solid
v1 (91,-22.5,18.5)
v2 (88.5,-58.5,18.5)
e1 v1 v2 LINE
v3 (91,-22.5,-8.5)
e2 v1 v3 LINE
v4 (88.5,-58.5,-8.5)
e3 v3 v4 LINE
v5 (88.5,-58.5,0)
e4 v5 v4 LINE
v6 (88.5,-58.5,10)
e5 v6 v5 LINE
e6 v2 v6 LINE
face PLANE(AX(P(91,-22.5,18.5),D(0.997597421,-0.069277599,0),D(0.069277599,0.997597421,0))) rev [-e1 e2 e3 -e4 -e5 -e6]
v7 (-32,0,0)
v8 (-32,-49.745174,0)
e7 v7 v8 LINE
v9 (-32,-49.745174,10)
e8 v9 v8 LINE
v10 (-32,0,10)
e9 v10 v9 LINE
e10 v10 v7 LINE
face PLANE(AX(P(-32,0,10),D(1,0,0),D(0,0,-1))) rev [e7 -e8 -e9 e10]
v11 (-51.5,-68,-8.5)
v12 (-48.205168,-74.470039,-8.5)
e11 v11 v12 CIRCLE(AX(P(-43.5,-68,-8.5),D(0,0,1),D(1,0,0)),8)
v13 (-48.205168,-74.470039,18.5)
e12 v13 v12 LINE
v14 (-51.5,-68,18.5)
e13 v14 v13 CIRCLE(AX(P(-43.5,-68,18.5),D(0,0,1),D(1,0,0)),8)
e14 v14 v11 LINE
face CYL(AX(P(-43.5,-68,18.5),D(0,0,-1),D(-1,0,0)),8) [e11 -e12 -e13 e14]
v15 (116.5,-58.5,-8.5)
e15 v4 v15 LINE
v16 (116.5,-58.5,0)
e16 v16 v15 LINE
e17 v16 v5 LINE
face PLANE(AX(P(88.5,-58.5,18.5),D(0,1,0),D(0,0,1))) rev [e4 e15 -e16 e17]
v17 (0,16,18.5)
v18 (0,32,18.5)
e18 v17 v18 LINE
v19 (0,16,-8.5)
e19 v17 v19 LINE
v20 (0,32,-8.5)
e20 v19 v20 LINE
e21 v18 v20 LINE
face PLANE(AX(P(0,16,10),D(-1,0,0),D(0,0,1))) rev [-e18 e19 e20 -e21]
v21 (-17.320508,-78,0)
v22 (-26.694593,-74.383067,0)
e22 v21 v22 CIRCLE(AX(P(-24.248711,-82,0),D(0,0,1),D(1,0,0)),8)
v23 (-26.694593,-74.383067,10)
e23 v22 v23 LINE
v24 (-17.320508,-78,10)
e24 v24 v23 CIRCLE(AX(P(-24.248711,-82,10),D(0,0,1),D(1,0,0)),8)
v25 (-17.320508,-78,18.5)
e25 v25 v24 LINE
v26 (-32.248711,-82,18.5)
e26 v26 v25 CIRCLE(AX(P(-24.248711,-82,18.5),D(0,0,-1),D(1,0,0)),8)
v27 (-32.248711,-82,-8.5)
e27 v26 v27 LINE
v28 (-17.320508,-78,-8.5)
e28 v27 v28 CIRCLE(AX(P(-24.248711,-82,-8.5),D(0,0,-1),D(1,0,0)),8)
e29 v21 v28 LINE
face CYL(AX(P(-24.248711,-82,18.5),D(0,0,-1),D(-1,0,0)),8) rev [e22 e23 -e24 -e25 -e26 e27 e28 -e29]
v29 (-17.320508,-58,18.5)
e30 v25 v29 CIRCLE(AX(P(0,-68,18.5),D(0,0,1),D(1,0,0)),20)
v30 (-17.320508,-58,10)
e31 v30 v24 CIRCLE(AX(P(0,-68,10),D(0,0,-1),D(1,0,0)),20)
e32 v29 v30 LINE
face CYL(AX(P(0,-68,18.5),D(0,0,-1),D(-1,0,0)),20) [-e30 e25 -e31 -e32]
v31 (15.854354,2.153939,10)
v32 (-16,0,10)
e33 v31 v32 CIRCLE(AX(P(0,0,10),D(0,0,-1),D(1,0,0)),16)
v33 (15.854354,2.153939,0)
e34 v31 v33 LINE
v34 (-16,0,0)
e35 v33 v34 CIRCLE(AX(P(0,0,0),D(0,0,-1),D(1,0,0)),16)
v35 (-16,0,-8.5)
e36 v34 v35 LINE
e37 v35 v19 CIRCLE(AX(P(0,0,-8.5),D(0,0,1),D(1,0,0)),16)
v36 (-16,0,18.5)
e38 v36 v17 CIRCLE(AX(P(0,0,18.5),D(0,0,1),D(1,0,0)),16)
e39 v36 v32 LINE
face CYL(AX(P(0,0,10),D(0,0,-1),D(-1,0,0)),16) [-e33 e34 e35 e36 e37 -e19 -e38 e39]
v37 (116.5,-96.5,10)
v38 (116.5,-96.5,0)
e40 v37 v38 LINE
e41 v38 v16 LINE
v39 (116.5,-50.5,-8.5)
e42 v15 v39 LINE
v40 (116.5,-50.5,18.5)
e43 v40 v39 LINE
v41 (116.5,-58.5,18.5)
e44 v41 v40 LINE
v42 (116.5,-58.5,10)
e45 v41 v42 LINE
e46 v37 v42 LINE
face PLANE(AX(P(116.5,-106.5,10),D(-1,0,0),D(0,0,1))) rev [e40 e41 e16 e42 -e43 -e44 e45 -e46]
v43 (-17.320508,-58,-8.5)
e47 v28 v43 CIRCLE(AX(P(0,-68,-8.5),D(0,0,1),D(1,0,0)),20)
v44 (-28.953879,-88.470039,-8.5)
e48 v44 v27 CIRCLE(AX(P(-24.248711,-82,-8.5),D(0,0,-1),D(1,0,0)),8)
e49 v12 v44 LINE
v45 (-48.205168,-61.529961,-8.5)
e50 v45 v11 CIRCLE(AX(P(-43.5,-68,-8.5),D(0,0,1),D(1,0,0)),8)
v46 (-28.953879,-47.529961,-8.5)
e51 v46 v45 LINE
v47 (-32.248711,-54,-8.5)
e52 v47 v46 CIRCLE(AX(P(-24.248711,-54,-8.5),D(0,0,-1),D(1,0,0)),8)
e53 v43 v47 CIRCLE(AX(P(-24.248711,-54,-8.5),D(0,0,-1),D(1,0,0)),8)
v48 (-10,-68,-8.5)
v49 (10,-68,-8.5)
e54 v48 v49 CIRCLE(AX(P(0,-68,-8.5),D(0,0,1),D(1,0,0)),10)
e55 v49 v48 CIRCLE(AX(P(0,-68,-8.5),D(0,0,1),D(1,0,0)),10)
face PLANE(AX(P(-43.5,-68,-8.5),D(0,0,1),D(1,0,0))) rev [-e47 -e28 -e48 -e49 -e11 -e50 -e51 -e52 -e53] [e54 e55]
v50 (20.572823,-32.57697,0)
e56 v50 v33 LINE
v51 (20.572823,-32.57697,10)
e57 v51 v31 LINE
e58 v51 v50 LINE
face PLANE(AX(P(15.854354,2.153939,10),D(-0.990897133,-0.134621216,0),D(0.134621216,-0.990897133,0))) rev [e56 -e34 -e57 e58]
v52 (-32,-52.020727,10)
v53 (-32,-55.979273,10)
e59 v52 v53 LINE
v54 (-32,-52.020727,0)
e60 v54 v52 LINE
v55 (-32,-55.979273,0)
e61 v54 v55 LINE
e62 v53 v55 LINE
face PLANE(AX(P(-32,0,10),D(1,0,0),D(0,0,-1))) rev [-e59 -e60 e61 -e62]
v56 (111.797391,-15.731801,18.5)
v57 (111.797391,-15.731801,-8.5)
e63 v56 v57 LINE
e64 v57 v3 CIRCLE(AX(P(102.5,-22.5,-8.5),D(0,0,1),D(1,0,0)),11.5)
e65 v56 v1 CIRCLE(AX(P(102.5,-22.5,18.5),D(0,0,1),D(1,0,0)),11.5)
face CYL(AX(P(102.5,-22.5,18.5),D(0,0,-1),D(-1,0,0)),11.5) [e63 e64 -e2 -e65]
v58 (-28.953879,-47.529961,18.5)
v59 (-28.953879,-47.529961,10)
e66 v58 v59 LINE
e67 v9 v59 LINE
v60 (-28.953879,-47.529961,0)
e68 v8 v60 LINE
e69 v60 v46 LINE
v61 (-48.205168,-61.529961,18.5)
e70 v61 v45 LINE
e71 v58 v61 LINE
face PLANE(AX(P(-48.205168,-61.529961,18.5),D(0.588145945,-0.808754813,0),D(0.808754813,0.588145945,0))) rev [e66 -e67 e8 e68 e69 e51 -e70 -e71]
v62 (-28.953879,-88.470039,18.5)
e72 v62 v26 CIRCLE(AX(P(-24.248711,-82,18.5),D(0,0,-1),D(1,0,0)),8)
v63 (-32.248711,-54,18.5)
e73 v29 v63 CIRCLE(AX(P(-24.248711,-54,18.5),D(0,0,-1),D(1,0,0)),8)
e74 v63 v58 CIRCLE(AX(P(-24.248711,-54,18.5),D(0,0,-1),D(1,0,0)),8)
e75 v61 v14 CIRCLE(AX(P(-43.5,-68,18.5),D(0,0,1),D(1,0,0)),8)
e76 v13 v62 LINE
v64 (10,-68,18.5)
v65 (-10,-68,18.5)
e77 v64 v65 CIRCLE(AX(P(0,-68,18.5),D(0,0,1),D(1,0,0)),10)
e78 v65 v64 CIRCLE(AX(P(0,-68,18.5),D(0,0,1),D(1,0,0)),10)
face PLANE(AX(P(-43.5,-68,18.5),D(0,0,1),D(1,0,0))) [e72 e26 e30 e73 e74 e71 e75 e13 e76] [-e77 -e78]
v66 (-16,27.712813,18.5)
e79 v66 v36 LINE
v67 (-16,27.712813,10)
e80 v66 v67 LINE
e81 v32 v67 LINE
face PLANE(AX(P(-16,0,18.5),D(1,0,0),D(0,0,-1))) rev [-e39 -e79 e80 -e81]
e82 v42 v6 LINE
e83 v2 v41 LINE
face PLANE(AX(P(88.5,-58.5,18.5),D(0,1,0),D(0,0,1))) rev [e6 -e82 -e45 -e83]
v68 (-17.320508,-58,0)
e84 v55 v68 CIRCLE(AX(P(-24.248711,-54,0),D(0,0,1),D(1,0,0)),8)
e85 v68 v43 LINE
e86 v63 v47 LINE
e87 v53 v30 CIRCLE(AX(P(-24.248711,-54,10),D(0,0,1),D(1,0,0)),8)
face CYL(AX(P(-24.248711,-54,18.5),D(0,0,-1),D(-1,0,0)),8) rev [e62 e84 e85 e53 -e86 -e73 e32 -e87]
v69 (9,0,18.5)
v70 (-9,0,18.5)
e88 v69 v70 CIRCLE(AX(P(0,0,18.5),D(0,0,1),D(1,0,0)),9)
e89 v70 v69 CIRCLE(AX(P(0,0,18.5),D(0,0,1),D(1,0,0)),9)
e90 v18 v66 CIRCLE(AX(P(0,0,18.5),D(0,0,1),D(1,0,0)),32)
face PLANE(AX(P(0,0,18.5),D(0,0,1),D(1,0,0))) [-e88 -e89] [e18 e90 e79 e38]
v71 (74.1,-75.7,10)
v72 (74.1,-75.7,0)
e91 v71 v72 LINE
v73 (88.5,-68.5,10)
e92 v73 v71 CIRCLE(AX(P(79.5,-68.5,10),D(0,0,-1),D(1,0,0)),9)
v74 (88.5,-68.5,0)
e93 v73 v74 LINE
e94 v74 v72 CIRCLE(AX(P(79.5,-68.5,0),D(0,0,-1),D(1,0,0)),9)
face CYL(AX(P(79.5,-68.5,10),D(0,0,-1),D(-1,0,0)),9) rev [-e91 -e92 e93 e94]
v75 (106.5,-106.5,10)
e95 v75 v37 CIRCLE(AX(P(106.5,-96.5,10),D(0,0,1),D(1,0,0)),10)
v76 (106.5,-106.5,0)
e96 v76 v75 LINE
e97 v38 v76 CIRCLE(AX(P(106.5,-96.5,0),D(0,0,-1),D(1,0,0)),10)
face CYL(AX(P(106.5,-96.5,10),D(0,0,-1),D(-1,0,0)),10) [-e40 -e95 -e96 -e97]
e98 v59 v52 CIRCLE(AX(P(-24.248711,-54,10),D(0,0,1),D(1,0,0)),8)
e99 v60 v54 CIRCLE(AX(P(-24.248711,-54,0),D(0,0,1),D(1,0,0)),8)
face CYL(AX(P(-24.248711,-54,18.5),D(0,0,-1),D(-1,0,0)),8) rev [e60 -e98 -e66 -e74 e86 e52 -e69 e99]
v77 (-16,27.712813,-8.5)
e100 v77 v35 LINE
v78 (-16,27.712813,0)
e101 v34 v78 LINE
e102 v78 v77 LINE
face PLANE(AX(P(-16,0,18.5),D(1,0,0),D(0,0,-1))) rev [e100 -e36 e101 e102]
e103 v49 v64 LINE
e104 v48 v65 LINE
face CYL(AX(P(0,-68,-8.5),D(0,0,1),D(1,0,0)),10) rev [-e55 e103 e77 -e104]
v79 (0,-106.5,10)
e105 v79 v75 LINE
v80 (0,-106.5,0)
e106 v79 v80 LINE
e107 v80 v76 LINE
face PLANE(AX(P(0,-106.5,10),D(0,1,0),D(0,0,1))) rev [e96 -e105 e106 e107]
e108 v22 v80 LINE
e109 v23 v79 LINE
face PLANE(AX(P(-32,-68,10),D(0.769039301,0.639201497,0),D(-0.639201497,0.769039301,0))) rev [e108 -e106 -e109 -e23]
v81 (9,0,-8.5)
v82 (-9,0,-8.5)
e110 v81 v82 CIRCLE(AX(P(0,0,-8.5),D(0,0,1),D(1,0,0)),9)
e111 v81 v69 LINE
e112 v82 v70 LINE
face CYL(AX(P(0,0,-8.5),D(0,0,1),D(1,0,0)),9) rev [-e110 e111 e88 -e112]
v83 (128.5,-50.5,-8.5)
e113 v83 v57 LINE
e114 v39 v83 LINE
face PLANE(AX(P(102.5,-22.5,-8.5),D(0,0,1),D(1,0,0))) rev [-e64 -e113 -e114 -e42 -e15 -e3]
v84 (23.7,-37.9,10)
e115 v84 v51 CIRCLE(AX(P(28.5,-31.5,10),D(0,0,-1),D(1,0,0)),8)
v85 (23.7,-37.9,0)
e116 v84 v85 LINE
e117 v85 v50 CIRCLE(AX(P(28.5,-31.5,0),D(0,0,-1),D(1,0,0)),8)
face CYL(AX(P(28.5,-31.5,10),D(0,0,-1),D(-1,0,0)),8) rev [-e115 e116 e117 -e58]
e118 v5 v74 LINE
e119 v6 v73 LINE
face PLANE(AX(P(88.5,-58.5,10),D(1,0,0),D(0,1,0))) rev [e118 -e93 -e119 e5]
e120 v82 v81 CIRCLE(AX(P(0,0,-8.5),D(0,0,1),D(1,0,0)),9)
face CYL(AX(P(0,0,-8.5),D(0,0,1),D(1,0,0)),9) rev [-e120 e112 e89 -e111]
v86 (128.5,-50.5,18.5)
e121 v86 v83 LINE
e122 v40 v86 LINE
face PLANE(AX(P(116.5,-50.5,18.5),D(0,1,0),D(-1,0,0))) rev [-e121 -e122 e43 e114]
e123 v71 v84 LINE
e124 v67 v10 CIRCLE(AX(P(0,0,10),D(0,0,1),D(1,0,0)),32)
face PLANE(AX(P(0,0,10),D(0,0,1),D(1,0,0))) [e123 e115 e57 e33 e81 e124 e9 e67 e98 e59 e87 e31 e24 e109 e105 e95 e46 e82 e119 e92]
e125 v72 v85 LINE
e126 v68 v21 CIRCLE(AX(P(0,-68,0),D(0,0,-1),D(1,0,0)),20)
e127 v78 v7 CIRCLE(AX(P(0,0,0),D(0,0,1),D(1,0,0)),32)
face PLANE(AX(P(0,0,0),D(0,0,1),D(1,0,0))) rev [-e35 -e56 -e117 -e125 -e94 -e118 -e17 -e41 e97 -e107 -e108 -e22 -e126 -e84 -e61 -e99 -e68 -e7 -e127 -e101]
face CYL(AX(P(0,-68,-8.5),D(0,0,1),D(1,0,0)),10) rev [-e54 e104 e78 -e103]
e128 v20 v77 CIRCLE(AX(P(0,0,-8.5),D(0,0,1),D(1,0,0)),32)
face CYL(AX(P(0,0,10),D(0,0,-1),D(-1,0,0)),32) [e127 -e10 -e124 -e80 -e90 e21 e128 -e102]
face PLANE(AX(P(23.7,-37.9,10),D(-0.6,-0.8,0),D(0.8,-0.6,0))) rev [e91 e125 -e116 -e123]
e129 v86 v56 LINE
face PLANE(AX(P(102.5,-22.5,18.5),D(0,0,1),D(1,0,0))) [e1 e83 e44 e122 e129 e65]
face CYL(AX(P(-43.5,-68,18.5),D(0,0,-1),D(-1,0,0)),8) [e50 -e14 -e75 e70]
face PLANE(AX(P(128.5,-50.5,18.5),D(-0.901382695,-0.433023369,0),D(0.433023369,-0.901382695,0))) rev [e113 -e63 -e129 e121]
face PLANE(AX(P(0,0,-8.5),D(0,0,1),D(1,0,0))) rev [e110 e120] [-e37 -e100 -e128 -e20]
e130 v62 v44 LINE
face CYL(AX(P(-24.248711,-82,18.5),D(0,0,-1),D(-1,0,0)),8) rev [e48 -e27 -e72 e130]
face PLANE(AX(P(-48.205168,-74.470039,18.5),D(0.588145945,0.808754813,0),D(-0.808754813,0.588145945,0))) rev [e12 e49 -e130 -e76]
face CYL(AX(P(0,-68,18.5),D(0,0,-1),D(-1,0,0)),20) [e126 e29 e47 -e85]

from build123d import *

# Parameters (mm, degrees)
BRACKET_PLATE_DEPTH        = 10
UPPER_PIVOT_BOSS_DEPTH     = 13.5
UPPER_PIVOT_BORE_PROFILE_R = 9
UPPER_PIVOT_BORE_18_DEPTH  = 27
LOWER_PIVOT_BOSS_DEPTH     = 13.5
LOWER_PIVOT_BORE_PROFILE_R = 10
LOWER_PIVOT_BORE_20_DEPTH  = 27
STOP_LUG_DEPTH             = 13.5
PLATE_FILLET_R10_R         = 10


with BuildPart() as part:
    # Bracket Plate Profile → Bracket Plate (new body)
    with BuildSketch(Plane.XY):
        with BuildLine():
            Line((-32, 0), (-32, -68))
            Line((-32, -68), (0, -106.5))
            Line((0, -106.5), (116.5, -106.5))
            Line((116.5, -106.5), (116.5, -58.5))
            Line((116.5, -58.5), (88.5, -58.5))
            Line((88.5, -58.5), (88.5, -68.5))
            ThreePointArc((88.5, -68.5), (83.524922359, -76.549844719), (74.1, -75.7))
            Line((74.1, -75.7), (23.7, -37.9))
            ThreePointArc((23.7, -37.9), (21.602252409, -35.552292952), (20.572822936, -32.576969725))
            Line((20.572822936, -32.576969725), (15.854354129, 2.15393945))
            ThreePointArc((15.854354129, 2.15393945), (10.524660774, 12.051203907), (0, 16))
            Line((0, 16), (0, 32))
            ThreePointArc((0, 32), (-22.627416998, 22.627416998), (-32, 0))
        make_face()
    extrude(amount=BRACKET_PLATE_DEPTH)

    # Upper Pivot Boss Profile → Upper Pivot Boss (add, symmetric)
    with BuildSketch(Plane.XY.offset(5)):
        with BuildLine():
            Line((0, 16), (0, 32))
            ThreePointArc((0, 32), (-8.282209443, 30.909626441), (-16, 27.712812921))
            Line((-16, 27.712812921), (-16, 0))
            ThreePointArc((-16, 0), (11.313708499, -11.313708499), (0, 16))
        make_face()
    extrude(amount=UPPER_PIVOT_BOSS_DEPTH, both=True)

    # Upper Pivot Bore Profile → Upper Pivot Bore Ø18 (cut)
    with BuildSketch(Plane.XY.offset(18.5)):
        Circle(UPPER_PIVOT_BORE_PROFILE_R)
    extrude(amount=-UPPER_PIVOT_BORE_18_DEPTH, mode=Mode.SUBTRACT)

    # Lower Pivot Boss Profile → Lower Pivot Boss (add, symmetric)
    with BuildSketch(Plane.XY.offset(5)):
        with BuildLine():
            Line((-48.20516756, -74.470038503), (-28.953878866, -88.470038503))
            ThreePointArc((-28.953878866, -88.470038503), (-29.600430512, -76.053648048), (-17.320508076, -78))
            ThreePointArc((-17.320508076, -78), (20, -68), (-17.320508076, -58))
            ThreePointArc((-17.320508076, -58), (-29.600430512, -59.946351952), (-28.953878866, -47.529961497))
            Line((-28.953878866, -47.529961497), (-48.20516756, -61.529961497))
            ThreePointArc((-48.20516756, -61.529961497), (-51.5, -68), (-48.20516756, -74.470038503))
        make_face()
    extrude(amount=LOWER_PIVOT_BOSS_DEPTH, both=True)

    # Lower Pivot Bore Profile → Lower Pivot Bore Ø20 (cut)
    with BuildSketch(Plane.XY.offset(18.5)):
        with Locations((0, -68)):
            Circle(LOWER_PIVOT_BORE_PROFILE_R)
    extrude(amount=-LOWER_PIVOT_BORE_20_DEPTH, mode=Mode.SUBTRACT)

    # Stop Lug Profile → Stop Lug (add, symmetric)
    with BuildSketch(Plane.XY.offset(5)):
        with BuildLine():
            Line((116.5, -58.5), (116.5, -50.5))
            Line((116.5, -50.5), (128.5, -50.5))
            Line((128.5, -50.5), (111.797390872, -15.731800611))
            ThreePointArc((111.797390872, -15.731800611), (98.941207721, -11.564507441), (91, -22.5))
            Line((91, -22.5), (88.5, -58.5))
            Line((88.5, -58.5), (116.5, -58.5))
        make_face()
    extrude(amount=STOP_LUG_DEPTH, both=True)

    # Plate Fillet R10
    plate_fillet_r10_edges = [part.edges().sort_by_distance(p)[0] for p in [
        (116.5, -106.5, 5),
    ]]
    fillet(plate_fillet_r10_edges, radius=PLATE_FILLET_R10_R)


solid = part.part
